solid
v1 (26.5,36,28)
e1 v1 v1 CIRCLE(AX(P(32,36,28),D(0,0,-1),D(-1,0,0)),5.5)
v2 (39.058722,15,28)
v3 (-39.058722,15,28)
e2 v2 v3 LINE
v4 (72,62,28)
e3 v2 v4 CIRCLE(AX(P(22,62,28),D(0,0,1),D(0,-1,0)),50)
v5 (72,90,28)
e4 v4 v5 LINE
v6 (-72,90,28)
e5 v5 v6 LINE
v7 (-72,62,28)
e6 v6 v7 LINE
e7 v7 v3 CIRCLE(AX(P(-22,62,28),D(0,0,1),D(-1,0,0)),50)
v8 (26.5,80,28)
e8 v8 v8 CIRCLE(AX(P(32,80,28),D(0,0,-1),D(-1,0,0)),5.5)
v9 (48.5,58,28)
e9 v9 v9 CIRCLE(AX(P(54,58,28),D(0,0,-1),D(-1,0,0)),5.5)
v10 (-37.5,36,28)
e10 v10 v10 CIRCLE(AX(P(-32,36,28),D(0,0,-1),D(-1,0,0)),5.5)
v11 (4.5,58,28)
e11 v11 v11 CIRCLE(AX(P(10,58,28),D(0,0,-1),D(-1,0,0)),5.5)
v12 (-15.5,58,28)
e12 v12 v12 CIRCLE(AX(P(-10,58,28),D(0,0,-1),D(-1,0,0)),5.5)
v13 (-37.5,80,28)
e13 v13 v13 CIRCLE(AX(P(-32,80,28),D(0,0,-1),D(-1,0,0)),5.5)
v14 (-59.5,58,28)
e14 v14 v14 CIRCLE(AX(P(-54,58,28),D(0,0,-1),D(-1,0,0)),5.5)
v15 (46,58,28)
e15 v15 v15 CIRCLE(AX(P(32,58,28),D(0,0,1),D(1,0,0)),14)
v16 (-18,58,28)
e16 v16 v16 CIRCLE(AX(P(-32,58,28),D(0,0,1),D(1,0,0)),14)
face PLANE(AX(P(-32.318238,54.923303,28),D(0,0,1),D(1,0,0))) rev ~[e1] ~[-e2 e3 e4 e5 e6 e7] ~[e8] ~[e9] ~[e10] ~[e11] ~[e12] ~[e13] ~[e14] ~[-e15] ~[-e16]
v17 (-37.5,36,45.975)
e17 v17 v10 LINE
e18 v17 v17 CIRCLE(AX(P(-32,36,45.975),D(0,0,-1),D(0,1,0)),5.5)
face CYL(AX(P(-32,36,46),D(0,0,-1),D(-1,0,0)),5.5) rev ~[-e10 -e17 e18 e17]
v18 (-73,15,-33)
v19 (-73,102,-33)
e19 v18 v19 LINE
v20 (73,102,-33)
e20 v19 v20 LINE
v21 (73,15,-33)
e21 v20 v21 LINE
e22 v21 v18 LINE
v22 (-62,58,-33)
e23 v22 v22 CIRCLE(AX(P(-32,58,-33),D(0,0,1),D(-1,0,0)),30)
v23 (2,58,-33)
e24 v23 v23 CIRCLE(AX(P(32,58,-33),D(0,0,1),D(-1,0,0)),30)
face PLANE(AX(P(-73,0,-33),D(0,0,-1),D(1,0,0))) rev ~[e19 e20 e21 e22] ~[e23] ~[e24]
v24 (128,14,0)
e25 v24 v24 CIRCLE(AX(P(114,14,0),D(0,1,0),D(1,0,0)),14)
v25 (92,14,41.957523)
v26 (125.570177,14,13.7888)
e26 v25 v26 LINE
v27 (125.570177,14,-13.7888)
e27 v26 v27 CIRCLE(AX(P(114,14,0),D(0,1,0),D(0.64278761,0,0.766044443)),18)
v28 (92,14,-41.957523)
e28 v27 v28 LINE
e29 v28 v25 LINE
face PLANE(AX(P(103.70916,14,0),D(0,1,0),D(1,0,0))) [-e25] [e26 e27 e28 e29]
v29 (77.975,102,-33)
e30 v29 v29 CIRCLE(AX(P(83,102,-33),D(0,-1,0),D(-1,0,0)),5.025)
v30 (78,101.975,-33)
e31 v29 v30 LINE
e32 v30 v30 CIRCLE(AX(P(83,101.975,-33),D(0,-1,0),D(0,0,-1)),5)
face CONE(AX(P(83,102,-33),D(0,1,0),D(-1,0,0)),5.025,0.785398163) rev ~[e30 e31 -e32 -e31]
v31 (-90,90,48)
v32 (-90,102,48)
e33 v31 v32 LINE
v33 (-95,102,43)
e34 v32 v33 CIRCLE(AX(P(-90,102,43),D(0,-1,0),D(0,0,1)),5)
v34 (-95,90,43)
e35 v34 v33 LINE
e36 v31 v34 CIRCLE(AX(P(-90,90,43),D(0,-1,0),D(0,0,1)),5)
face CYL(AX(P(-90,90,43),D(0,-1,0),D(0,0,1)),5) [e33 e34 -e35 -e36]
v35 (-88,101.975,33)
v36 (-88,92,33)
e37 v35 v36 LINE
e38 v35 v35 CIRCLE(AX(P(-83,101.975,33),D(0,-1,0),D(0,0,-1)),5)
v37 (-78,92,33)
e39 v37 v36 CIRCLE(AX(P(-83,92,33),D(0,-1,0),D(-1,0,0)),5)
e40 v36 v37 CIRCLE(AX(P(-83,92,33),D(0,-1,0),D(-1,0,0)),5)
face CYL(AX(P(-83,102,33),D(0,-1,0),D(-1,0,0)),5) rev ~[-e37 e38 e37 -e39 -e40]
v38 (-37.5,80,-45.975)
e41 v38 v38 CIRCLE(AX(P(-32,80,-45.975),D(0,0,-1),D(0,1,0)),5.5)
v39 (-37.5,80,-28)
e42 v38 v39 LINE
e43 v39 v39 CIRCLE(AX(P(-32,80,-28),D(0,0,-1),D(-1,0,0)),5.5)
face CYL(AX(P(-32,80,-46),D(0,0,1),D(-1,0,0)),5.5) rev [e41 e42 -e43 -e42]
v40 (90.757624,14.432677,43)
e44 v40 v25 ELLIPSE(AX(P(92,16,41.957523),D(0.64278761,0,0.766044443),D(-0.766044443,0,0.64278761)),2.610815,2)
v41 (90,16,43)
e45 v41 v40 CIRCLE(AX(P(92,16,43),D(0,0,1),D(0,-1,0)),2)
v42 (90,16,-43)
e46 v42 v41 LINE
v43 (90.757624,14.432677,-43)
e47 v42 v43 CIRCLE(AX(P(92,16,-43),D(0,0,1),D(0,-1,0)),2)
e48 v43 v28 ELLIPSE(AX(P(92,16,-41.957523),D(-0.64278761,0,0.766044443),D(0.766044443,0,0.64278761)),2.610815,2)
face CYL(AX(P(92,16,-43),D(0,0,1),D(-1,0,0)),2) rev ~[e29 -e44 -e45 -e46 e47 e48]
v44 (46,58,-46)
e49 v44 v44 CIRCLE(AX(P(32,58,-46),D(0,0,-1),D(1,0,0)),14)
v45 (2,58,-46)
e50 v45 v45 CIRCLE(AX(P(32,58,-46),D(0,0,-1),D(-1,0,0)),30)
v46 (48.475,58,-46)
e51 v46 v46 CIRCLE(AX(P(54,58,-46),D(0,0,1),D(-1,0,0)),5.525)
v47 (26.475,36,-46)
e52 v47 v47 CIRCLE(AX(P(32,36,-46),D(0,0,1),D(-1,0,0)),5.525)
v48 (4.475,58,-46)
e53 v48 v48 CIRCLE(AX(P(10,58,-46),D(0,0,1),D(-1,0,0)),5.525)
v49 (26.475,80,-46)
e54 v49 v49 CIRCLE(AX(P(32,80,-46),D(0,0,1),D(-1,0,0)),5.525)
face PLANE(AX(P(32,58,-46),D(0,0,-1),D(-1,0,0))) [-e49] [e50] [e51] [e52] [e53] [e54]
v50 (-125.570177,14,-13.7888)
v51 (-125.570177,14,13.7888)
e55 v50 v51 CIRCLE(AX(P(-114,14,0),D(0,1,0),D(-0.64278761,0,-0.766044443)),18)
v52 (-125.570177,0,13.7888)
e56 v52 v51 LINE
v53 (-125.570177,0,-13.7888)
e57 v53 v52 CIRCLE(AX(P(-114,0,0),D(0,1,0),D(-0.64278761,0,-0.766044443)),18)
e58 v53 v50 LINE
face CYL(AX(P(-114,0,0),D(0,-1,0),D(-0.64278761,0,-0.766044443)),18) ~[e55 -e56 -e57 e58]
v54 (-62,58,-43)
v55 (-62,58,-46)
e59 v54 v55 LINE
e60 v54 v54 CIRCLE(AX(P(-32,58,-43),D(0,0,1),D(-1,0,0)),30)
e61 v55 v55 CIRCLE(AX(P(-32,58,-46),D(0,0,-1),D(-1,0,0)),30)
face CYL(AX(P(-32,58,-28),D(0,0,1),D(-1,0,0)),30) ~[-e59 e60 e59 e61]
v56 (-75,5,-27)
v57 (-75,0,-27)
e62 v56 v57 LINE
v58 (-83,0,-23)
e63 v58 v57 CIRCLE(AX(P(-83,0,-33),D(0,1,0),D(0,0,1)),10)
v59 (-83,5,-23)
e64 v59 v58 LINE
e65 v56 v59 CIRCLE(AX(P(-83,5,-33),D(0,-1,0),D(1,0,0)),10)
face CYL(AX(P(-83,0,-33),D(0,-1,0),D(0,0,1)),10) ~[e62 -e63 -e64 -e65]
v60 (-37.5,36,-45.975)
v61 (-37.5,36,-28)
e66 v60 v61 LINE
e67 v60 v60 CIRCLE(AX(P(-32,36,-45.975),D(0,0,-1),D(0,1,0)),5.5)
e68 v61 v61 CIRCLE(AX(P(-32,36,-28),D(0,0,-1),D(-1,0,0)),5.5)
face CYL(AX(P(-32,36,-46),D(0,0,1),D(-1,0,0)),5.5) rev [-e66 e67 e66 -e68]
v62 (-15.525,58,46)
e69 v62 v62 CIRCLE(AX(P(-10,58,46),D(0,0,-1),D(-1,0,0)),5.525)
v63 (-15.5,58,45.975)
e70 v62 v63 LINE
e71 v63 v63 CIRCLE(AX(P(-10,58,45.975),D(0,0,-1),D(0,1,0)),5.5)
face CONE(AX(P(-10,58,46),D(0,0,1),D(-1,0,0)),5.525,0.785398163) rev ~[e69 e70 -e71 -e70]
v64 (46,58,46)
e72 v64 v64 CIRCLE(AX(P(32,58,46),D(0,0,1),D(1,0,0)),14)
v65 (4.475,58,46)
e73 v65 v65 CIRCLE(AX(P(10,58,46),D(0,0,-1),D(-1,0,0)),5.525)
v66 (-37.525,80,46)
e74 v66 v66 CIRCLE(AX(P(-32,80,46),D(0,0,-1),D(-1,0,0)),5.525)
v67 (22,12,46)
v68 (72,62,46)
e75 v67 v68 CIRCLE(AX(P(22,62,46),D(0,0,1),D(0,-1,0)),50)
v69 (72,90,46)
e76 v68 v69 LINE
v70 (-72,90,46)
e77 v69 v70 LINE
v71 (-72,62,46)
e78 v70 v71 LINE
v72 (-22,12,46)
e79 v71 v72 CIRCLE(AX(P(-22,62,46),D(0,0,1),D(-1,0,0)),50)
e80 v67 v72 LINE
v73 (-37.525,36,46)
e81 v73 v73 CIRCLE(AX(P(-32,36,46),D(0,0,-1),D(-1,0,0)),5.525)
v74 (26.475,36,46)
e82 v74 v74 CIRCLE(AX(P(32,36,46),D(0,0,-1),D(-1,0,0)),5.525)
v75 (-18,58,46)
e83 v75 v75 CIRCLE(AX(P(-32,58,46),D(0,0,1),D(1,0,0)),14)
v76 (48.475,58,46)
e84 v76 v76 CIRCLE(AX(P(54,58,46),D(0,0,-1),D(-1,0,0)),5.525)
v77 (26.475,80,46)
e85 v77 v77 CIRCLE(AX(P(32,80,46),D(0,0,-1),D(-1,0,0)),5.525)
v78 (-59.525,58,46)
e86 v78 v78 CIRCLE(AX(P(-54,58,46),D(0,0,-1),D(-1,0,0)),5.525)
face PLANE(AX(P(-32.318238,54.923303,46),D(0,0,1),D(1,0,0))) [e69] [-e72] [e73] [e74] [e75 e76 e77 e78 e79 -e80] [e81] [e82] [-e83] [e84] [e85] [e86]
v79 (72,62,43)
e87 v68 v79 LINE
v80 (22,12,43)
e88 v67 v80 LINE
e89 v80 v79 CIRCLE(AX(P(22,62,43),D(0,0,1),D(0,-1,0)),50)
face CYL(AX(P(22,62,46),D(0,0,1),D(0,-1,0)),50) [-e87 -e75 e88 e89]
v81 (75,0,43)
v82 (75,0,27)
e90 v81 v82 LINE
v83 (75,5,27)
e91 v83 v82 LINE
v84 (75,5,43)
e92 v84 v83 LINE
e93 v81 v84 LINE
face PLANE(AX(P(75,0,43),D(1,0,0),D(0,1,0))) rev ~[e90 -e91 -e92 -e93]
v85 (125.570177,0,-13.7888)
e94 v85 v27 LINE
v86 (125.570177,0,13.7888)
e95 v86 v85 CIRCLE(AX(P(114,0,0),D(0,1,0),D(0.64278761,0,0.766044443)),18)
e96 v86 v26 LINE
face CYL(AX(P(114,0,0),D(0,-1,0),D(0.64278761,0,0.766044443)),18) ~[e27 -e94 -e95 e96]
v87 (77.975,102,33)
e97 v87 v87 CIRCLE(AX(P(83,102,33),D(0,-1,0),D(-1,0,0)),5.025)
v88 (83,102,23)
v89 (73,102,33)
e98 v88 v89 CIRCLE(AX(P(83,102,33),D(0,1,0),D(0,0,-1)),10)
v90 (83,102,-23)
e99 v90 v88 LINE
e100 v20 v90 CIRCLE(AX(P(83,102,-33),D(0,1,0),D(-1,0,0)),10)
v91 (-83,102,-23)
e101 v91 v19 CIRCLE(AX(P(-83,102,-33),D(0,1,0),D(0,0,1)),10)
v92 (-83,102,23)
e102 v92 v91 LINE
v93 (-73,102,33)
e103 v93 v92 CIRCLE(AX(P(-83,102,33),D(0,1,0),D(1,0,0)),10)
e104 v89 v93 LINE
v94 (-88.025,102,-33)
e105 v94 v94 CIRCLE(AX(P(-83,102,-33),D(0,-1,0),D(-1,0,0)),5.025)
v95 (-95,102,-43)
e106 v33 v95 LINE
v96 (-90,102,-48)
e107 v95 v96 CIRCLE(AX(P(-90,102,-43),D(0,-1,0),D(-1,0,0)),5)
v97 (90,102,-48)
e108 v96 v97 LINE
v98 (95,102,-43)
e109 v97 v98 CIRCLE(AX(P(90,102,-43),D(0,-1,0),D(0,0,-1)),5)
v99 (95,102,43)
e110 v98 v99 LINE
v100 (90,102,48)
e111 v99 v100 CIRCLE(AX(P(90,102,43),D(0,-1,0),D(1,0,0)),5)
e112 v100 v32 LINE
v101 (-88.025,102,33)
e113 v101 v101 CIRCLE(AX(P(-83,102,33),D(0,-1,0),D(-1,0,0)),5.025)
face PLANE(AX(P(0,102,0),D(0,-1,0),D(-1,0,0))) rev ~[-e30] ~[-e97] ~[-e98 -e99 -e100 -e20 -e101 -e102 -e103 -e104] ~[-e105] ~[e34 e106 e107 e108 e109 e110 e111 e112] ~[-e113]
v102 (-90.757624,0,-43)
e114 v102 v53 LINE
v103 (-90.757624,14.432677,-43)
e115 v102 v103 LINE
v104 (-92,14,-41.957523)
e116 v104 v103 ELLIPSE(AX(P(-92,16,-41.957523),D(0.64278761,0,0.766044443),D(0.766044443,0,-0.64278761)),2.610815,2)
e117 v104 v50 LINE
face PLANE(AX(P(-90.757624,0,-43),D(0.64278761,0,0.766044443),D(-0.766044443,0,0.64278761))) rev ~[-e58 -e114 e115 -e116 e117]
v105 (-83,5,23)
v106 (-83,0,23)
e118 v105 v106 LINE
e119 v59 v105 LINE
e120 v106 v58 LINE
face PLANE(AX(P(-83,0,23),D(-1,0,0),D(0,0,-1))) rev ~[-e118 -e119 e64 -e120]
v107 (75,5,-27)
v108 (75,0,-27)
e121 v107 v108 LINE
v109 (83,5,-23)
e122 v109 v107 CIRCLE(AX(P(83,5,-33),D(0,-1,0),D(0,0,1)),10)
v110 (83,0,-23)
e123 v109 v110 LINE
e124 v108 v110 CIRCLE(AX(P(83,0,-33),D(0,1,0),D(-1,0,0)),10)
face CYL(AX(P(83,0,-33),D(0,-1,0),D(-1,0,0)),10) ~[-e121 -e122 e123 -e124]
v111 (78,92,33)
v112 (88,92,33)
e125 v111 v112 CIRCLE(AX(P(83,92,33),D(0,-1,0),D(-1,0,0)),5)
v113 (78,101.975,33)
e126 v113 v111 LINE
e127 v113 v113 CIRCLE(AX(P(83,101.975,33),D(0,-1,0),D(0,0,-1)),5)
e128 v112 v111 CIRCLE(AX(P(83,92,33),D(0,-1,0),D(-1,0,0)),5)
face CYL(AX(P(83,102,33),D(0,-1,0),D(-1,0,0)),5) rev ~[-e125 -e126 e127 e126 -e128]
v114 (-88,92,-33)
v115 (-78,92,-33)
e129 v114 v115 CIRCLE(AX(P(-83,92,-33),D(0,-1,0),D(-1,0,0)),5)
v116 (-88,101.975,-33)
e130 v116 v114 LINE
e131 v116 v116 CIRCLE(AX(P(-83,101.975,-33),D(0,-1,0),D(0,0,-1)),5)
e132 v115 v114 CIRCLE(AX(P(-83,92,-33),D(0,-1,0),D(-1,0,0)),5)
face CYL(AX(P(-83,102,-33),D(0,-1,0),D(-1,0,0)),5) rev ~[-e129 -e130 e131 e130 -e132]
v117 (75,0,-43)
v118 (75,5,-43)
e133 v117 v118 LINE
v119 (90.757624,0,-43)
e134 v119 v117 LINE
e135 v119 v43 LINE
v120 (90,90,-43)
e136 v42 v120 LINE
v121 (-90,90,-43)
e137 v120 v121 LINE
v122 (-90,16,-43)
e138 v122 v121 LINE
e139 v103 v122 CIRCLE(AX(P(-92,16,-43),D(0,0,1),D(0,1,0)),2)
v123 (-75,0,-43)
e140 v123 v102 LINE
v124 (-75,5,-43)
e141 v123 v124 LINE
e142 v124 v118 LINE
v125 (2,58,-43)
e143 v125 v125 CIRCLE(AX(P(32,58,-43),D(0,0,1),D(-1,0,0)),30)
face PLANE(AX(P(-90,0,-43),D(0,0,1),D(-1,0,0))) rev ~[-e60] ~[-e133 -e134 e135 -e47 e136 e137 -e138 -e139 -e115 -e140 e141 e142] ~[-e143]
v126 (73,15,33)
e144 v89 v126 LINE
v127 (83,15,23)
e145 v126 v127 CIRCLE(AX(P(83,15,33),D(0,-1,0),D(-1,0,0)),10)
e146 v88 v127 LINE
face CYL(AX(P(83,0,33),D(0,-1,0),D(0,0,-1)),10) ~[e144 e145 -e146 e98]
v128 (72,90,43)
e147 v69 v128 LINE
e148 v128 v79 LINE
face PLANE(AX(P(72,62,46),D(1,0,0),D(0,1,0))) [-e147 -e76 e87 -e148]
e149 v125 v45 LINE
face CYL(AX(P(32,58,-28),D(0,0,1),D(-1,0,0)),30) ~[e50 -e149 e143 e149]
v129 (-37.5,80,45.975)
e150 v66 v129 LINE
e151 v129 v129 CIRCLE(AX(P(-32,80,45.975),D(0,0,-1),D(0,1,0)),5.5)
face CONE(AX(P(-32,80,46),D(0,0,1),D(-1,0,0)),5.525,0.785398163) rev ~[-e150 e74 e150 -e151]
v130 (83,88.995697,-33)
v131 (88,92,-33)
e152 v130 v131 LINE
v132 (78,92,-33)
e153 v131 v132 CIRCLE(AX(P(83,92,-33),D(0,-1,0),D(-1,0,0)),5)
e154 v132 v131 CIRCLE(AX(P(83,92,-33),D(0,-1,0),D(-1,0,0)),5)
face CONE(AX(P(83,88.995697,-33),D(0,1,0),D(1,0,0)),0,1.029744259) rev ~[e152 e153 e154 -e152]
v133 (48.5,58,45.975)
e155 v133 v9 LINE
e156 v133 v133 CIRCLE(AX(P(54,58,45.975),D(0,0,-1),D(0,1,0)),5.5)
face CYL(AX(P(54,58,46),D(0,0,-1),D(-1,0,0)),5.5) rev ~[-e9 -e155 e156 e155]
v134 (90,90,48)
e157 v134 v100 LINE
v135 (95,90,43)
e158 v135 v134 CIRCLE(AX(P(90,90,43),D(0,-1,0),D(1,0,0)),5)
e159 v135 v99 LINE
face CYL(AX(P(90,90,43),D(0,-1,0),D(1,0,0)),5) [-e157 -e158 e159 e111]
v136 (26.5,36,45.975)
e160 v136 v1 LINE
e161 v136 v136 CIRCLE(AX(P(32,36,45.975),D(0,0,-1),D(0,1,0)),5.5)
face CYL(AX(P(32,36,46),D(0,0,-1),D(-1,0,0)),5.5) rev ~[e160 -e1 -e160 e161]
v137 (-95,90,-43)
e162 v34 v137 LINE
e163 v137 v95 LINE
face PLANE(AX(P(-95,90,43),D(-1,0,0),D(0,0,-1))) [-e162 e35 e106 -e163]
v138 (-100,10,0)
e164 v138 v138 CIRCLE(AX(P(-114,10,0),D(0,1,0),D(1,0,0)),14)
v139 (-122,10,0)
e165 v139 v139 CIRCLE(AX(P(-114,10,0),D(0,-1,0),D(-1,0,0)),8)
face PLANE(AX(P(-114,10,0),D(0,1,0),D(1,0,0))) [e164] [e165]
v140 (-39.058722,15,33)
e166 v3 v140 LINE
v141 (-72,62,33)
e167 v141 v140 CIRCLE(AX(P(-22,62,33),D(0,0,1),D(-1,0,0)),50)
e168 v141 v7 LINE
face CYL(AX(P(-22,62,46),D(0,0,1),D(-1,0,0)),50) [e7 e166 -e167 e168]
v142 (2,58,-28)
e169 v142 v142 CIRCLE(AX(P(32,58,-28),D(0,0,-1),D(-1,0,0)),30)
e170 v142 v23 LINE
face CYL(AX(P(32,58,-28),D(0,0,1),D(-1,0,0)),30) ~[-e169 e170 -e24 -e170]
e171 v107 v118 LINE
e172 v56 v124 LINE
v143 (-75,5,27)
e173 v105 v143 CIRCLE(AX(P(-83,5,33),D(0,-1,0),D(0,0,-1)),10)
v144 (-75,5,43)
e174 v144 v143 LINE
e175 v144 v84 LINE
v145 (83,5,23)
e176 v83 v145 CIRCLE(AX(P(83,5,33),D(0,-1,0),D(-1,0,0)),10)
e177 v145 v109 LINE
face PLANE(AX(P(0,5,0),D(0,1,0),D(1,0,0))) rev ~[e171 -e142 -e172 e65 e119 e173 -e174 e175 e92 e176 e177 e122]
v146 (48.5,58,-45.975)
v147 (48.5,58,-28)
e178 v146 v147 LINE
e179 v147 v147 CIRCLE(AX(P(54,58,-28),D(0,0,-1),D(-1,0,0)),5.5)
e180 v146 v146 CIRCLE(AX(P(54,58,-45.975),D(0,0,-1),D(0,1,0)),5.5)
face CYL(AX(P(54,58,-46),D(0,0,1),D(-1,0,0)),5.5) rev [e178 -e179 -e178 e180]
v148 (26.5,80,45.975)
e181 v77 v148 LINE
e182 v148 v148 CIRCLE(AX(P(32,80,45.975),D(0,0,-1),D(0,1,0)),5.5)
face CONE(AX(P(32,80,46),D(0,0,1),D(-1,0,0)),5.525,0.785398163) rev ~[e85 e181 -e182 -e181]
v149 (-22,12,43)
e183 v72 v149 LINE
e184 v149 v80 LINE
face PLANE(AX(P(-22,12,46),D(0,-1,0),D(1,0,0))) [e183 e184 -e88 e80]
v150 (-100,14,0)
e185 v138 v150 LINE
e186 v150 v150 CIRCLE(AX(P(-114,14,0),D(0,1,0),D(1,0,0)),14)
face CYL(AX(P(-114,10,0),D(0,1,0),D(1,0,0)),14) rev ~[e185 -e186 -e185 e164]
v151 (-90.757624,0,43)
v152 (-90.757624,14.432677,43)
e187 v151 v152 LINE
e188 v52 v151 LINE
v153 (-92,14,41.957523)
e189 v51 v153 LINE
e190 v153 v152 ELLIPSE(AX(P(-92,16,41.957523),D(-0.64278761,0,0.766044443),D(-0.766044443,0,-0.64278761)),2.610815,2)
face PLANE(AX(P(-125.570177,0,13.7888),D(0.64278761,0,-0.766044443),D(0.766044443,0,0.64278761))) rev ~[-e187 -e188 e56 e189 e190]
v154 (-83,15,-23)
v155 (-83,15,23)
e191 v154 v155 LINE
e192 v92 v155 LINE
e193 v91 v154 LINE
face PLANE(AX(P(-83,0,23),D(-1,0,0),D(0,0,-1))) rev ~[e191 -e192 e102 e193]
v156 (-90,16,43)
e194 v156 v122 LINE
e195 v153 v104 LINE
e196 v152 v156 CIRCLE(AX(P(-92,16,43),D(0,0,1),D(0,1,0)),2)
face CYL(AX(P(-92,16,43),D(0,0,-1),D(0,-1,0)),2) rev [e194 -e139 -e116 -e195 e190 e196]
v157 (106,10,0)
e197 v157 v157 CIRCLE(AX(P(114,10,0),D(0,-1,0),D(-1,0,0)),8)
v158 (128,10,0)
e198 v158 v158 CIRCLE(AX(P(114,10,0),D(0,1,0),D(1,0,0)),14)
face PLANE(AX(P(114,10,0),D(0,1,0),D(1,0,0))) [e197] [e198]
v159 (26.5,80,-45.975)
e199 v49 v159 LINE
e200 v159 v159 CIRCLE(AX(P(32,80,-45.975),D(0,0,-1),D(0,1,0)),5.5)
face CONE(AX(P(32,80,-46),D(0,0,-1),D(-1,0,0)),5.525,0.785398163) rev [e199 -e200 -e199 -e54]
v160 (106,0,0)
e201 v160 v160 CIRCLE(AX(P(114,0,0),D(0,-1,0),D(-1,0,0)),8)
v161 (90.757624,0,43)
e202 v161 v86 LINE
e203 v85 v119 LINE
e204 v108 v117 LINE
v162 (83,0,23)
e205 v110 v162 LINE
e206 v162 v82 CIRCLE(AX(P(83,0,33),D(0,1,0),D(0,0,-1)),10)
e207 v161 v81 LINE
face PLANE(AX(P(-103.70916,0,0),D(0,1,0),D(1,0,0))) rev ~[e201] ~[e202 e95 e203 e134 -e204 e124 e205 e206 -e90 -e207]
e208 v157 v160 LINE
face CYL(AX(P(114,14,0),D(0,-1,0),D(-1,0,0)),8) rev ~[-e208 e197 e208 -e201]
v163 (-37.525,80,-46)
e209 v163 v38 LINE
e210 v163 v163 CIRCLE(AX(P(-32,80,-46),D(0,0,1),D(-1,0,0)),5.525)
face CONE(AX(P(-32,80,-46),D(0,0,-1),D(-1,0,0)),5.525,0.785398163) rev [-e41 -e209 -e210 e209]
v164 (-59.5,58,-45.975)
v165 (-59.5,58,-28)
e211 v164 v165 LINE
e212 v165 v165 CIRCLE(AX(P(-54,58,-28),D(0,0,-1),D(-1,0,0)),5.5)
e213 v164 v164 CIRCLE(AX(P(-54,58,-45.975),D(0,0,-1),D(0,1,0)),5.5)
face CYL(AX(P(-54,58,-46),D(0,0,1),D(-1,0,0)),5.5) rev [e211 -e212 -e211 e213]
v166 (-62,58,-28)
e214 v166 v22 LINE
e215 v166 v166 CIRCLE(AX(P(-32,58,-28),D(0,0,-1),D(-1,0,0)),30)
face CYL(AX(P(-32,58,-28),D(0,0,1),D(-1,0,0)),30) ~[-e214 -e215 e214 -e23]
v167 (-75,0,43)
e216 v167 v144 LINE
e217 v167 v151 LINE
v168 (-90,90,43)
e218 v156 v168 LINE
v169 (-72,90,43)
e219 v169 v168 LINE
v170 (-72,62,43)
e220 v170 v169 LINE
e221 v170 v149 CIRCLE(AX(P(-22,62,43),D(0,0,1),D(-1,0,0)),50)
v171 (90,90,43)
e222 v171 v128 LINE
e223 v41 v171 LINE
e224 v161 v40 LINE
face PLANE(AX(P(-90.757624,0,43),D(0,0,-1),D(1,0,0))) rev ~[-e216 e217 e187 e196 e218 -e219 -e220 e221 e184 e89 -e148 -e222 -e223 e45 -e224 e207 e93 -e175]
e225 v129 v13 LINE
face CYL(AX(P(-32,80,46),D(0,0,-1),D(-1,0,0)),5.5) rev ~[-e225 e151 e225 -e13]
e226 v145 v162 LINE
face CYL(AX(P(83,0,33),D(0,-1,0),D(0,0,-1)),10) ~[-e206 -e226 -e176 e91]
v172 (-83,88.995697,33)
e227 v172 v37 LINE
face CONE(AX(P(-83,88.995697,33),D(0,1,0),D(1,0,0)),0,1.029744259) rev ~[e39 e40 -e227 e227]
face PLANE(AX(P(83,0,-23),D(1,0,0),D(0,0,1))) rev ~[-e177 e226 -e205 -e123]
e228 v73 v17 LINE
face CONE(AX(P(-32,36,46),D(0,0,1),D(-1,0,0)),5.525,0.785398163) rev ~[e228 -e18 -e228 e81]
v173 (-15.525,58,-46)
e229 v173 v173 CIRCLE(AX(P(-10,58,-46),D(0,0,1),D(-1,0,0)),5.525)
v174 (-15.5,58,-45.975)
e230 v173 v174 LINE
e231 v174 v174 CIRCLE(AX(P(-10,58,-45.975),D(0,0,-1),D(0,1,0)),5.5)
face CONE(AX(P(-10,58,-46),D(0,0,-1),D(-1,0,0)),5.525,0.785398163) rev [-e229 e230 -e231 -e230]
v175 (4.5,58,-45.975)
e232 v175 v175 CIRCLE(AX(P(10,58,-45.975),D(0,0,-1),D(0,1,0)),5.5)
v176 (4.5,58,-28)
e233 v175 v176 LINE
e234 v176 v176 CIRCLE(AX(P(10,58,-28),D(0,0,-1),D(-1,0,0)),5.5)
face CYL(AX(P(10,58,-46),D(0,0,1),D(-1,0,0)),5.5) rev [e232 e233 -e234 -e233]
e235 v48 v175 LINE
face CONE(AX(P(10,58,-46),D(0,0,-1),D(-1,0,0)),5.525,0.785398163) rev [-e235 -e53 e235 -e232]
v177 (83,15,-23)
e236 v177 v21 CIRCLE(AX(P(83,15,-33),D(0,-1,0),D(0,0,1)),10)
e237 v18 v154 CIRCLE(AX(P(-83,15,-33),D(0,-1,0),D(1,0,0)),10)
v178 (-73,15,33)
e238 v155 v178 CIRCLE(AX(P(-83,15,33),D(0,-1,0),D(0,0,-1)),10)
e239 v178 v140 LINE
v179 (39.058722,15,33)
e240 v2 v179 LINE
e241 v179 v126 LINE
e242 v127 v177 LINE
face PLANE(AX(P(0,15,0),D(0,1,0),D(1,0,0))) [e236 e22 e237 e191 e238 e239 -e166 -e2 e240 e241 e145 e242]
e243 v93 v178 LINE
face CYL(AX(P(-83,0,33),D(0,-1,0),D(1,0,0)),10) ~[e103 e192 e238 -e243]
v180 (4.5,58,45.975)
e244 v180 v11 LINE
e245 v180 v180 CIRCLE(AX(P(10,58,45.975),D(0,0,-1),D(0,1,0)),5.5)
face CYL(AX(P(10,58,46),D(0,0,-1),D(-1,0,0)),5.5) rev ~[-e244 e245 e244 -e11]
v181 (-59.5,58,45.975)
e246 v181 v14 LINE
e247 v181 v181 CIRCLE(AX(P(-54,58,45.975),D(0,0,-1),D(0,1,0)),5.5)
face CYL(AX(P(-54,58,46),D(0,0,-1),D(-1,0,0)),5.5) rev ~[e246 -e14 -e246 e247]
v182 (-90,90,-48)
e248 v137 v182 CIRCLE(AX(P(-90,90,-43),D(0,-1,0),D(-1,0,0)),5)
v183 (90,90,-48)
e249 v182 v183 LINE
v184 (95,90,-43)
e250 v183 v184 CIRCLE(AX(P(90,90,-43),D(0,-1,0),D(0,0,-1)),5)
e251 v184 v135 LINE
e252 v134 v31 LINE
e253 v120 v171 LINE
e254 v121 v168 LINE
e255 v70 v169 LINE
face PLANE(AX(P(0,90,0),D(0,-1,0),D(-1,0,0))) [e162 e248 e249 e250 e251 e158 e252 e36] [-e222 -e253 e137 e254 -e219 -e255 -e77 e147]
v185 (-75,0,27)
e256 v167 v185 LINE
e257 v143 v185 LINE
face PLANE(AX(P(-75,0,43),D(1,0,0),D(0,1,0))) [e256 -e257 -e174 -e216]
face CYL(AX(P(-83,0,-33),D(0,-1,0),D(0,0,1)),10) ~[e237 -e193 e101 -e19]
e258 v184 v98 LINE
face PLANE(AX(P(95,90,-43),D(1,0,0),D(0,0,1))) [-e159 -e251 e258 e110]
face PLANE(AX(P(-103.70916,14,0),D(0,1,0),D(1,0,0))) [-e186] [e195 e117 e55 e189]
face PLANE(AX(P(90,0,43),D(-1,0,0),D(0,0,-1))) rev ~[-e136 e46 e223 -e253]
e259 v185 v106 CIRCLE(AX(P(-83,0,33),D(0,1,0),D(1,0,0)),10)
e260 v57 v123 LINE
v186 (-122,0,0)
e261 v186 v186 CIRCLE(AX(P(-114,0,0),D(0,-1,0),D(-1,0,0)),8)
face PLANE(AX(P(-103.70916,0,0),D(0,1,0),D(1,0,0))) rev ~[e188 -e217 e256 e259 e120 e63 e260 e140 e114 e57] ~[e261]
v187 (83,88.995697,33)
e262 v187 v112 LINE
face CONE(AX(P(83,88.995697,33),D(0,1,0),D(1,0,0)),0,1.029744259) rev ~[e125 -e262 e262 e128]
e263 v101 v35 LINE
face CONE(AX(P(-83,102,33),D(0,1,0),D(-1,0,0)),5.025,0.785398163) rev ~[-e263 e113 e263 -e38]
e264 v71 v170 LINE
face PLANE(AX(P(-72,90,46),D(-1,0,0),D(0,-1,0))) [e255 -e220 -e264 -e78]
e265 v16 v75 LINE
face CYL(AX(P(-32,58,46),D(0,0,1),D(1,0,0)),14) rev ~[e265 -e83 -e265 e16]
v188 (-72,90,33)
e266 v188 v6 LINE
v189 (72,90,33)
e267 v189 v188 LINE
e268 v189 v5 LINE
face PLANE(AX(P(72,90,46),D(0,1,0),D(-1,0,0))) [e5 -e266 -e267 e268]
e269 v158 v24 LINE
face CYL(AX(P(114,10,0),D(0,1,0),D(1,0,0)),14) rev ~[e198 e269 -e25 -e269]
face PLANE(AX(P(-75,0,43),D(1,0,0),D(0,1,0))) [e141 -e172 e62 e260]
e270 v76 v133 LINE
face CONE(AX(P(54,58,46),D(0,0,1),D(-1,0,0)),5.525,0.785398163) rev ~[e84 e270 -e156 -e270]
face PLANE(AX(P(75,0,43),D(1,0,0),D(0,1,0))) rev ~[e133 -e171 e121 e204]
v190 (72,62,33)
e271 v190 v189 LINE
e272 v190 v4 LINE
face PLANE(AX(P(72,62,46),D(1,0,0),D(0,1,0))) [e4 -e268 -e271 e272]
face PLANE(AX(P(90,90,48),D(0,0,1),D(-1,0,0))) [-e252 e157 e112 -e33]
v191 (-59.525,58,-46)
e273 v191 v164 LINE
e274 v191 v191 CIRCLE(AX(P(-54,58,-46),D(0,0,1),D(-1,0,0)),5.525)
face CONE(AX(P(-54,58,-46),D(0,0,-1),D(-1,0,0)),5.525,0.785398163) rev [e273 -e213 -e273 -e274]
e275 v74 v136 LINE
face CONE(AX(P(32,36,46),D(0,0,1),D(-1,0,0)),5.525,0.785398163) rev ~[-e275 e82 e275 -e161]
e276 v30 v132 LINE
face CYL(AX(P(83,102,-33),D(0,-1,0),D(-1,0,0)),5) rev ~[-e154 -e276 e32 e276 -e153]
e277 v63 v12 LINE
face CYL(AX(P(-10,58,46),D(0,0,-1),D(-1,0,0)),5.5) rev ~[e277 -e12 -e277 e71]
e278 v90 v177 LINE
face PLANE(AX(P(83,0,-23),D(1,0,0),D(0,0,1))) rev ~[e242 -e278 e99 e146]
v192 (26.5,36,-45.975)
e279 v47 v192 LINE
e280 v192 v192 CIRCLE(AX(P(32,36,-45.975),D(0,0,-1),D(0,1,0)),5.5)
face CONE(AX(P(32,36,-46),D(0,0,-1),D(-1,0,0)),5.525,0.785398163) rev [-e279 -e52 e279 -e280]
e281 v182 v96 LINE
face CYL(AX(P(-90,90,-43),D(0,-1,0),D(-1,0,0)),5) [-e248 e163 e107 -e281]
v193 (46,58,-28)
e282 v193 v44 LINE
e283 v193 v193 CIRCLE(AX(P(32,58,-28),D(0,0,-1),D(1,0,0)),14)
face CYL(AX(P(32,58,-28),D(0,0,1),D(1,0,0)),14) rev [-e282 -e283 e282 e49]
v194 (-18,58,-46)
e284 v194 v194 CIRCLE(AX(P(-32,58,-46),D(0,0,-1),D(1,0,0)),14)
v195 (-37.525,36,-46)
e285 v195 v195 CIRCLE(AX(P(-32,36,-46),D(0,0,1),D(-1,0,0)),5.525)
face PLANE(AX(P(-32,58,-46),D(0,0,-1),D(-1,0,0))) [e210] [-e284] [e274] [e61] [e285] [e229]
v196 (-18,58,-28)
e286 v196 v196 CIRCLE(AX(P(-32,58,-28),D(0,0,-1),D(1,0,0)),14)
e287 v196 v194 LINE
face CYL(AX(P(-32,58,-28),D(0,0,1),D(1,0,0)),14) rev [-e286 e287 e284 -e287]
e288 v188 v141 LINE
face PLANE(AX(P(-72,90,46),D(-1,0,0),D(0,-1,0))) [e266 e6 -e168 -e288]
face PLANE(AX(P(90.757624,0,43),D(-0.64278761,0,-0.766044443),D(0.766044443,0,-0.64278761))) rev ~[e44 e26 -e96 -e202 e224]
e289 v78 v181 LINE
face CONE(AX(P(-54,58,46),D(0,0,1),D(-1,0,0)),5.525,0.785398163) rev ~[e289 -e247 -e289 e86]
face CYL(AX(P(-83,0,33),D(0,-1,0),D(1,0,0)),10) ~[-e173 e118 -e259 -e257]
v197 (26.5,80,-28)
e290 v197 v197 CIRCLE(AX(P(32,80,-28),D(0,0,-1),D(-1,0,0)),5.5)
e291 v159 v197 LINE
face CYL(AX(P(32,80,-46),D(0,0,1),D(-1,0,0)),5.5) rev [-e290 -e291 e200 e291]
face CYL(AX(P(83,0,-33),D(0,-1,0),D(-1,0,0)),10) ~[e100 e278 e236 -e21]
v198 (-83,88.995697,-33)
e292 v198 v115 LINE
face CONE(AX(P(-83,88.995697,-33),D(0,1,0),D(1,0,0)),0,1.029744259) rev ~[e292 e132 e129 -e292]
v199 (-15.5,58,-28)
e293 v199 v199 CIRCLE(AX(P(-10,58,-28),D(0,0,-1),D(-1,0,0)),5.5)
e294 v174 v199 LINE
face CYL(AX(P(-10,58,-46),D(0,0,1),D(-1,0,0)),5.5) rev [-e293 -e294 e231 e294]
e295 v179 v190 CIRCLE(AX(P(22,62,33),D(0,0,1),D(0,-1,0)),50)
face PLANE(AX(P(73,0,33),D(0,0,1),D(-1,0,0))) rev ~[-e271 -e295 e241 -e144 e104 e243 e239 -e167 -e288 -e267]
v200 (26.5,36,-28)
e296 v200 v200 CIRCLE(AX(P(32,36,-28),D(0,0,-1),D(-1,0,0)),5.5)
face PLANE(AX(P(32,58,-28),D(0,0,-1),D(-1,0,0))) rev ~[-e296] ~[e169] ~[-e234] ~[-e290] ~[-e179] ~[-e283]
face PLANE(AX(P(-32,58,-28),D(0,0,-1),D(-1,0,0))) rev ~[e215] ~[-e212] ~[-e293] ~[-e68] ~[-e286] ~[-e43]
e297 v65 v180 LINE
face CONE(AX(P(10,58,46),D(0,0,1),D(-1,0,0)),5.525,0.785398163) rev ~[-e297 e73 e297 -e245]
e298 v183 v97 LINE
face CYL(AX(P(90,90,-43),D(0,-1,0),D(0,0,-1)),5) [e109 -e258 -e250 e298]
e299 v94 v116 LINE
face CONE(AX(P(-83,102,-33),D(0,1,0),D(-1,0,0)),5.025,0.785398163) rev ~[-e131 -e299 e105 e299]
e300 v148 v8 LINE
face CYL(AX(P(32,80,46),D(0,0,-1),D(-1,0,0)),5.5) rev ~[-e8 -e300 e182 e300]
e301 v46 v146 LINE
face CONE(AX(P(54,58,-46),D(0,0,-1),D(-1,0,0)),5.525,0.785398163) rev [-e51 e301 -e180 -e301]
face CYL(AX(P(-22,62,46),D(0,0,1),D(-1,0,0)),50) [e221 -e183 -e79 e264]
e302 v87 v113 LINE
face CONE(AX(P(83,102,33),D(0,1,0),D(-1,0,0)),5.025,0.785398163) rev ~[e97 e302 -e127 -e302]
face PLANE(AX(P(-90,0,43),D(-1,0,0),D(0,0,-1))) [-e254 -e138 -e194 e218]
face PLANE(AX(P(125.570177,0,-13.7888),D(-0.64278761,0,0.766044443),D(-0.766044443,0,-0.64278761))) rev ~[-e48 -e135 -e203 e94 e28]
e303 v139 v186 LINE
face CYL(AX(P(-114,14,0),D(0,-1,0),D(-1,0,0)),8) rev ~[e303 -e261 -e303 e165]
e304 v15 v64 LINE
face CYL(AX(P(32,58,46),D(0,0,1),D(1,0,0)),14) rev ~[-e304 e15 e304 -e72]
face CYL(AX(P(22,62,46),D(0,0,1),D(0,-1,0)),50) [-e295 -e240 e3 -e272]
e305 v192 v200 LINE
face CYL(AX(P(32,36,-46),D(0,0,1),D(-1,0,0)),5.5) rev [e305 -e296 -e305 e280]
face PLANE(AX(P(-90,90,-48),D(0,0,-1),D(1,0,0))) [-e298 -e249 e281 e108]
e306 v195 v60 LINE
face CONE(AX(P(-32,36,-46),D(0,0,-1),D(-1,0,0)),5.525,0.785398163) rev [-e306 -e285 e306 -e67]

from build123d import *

# Parameters (mm, degrees)
HOUSING_BASE_PROFILE_SKETCH_W          = 180
HOUSING_BASE_PROFILE_SKETCH_H          = 86
HOUSING_BODY_DEPTH                     = 102
TOP_START                              = -12
TOP_FLANGE_DEPTH                       = 12
MOUNTING_FOOT_LUGS_DEPTH               = 14
SIDE_START                             = 3
SIDE_FLANGE_PAD_SKETCH_R               = 14
SIDE_FLANGE_PADS_DEPTH                 = 18
BEARING_START                          = -15
BEARING_BOSS_60_SKETCH_R               = 30
BEARING_BOSS_60_SKETCH_R_2             = 14
BEARING_BOSSES_60_DEPTH                = 18
SKETCH6_2_R                            = 14
BEARING_BORES_DEPTH                    = 191.023682735
HOUSING_CAVITY_SKETCH_W                = 150
HOUSING_CAVITY_SKETCH_H                = 5
HOUSING_CAVITY_DEPTH                   = 191.023682735
BASE_START                             = 5
BASE_PROFILE_PAD_10MM_DEPTH            = 10
FOOT_COUNTERBORED_HOLES_16_D           = 16
FOOT_COUNTERBORED_HOLES_16_CBORE_D     = 28
FOOT_COUNTERBORED_HOLES_16_CBORE_DEPTH = 4
DOWEL_HOLES_10_D                       = 10
DOWEL_HOLES_10_DEPTH                   = 10
DOWEL_HOLES_10_CSINK_D                 = 10.05
DOWEL_HOLES_10_CSINK_ANGLE             = 90
DOWEL_HOLES_10_TIP                     = 3.004303095
FLANGE_BOLT_HOLES_M10_D                = 11
FLANGE_BOLT_HOLES_M10_DEPTH            = 18
FLANGE_BOLT_HOLES_M10_CSINK_D          = 11.05
FLANGE_BOLT_HOLES_M10_CSINK_ANGLE      = 90
FOOT_FILLETS_R2_R                      = 2


with BuildPart() as part:
    # Housing Base Profile Sketch → Housing Body (new body)
    with BuildSketch(Plane(origin=(0, 0, 0), x_dir=(1, 0, 0), z_dir=(0, 1, 0))):
        Rectangle(HOUSING_BASE_PROFILE_SKETCH_W, HOUSING_BASE_PROFILE_SKETCH_H)
        with BuildLine():
            Line((-73, 33), (73, 33))
            ThreePointArc((73, 33), (75.928932188, 25.928932188), (83, 23))
            Line((83, 23), (83, -23))
            ThreePointArc((83, -23), (75.928932188, -25.928932188), (73, -33))
            Line((73, -33), (-73, -33))
            ThreePointArc((-73, -33), (-75.928932188, -25.928932188), (-83, -23))
            Line((-83, -23), (-83, 23))
            ThreePointArc((-83, 23), (-75.928932188, 25.928932188), (-73, 33))
        make_face(mode=Mode.SUBTRACT)
    extrude(amount=HOUSING_BODY_DEPTH)

    # Top Flange Sketch → Top Flange (add)
    with BuildSketch(Plane(origin=(0, 102, 0), x_dir=(1, 0, 0), z_dir=(0, 1, 0)).offset(TOP_START)):
        with BuildLine():
            Line((-90, 48), (90, 48))
            ThreePointArc((90, 48), (93.535533906, 46.535533906), (95, 43))
            Line((95, 43), (95, -43))
            ThreePointArc((95, -43), (93.535533906, -46.535533906), (90, -48))
            Line((90, -48), (-90, -48))
            ThreePointArc((-90, -48), (-93.535533906, -46.535533906), (-95, -43))
            Line((-95, -43), (-95, 43))
            ThreePointArc((-95, 43), (-93.535533906, 46.535533906), (-90, 48))
        make_face()
        with BuildLine():
            Line((-73, 33), (73, 33))
            ThreePointArc((73, 33), (75.928932188, 25.928932188), (83, 23))
            Line((83, 23), (83, -23))
            ThreePointArc((83, -23), (75.928932188, -25.928932188), (73, -33))
            Line((73, -33), (-73, -33))
            ThreePointArc((-73, -33), (-75.928932188, -25.928932188), (-83, -23))
            Line((-83, -23), (-83, 23))
            ThreePointArc((-83, 23), (-75.928932188, 25.928932188), (-73, 33))
        make_face(mode=Mode.SUBTRACT)
    extrude(amount=TOP_FLANGE_DEPTH)

    # Sketch2_4 → Mounting Foot Lugs (add)
    with BuildSketch(Plane(origin=(0, 0, 0), x_dir=(1, 0, 0), z_dir=(0, 1, 0))):
        with BuildLine():
            Line((-90, -43), (-90, 43))
            Line((-90, 43), (-90.757624402, 43))
            Line((-90.757624402, 43), (-125.570176974, 13.788799976))
            ThreePointArc((-125.570176974, 13.788799976), (-132, 0), (-125.570176974, -13.788799976))
            Line((-125.570176974, -13.788799976), (-90.757624402, -43))
            Line((-90.757624402, -43), (-90, -43))
        make_face()
        with BuildLine():
            Line((90.757624402, 43), (90, 43))
            Line((90, 43), (90, -43))
            Line((90, -43), (90.757624402, -43))
            Line((90.757624402, -43), (125.570176974, -13.788799976))
            ThreePointArc((125.570176974, -13.788799976), (132, 0), (125.570176974, 13.788799976))
            Line((125.570176974, 13.788799976), (90.757624402, 43))
        make_face()
    extrude(amount=MOUNTING_FOOT_LUGS_DEPTH)

    # Side Flange Pad Sketch → Side Flange Pads (add)
    # profile 1 of 2: a face of its own
    with BuildSketch(Plane.XY.offset(43).offset(SIDE_START)):
        with BuildLine():
            Line((-22, 12), (0, 12))
            Line((0, 12), (0, 90))
            Line((0, 90), (-72, 90))
            Line((-72, 90), (-72, 62))
            ThreePointArc((-72, 62), (-57.355339059, 26.644660941), (-22, 12))
        make_face()
        with Locations((-32, 58)):
            Circle(SIDE_FLANGE_PAD_SKETCH_R, mode=Mode.SUBTRACT)
    # profile 2 of 2: a face of its own
    with BuildSketch(Plane.XY.offset(43).offset(SIDE_START)):
        with BuildLine():
            Line((0, 90), (0, 12))
            Line((0, 12), (22, 12))
            ThreePointArc((22, 12), (57.355339059, 26.644660941), (72, 62))
            Line((72, 62), (72, 90))
            Line((72, 90), (0, 90))
        make_face()
        with Locations((32, 58)):
            Circle(SIDE_FLANGE_PAD_SKETCH_R, mode=Mode.SUBTRACT)
    extrude(amount=-SIDE_FLANGE_PADS_DEPTH)

    # Bearing Boss _60 Sketch → Bearing Bosses _60 (add)
    # profile 1 of 2: a face of its own
    with BuildSketch(Plane(origin=(0, 0, -43), x_dir=(-1, 0, 0), z_dir=(0, 0, -1)).offset(BEARING_START)):
        with Locations((-32, 58)):
            Circle(BEARING_BOSS_60_SKETCH_R)
        with Locations(Location((-32, 58, 0), (0, 0, 180))):
            Circle(BEARING_BOSS_60_SKETCH_R_2, mode=Mode.SUBTRACT)
    # profile 2 of 2: a face of its own
    with BuildSketch(Plane(origin=(0, 0, -43), x_dir=(-1, 0, 0), z_dir=(0, 0, -1)).offset(BEARING_START)):
        with Locations((32, 58)):
            Circle(BEARING_BOSS_60_SKETCH_R)
        with Locations(Location((32, 58, 0), (0, 0, 180))):
            Circle(BEARING_BOSS_60_SKETCH_R_2, mode=Mode.SUBTRACT)
    extrude(amount=BEARING_BOSSES_60_DEPTH)

    # Sketch6_2 → Bearing Bores (cut, through all)
    with BuildSketch(Plane(origin=(0, 0, -43), x_dir=(-1, 0, 0), z_dir=(0, 0, -1))):
        with Locations(Location((32, 58, 0), (0, 0, 180))):
            Circle(SKETCH6_2_R)
        with Locations(Location((-32, 58, 0), (0, 0, 180))):
            Circle(SKETCH6_2_R)
    extrude(amount=-BEARING_BORES_DEPTH, mode=Mode.SUBTRACT)

    # Housing Cavity Sketch → Housing Cavity (cut, through all)
    with BuildSketch(Plane.XY.offset(43)):
        with Locations((0, 2.5)):
            Rectangle(HOUSING_CAVITY_SKETCH_W, HOUSING_CAVITY_SKETCH_H)
    extrude(amount=-HOUSING_CAVITY_DEPTH, mode=Mode.SUBTRACT)

    # Sketch2_5 → Base Profile Pad 10mm (add)
    with BuildSketch(Plane(origin=(0, 0, 0), x_dir=(1, 0, 0), z_dir=(0, 1, 0)).offset(BASE_START)):
        with BuildLine():
            Line((-83, 23), (-83, -23))
            ThreePointArc((-83, -23), (-75.928932188, -25.928932188), (-73, -33))
            Line((-73, -33), (73, -33))
            ThreePointArc((73, -33), (75.928932188, -25.928932188), (83, -23))
            Line((83, -23), (83, 23))
            ThreePointArc((83, 23), (75.928932188, 25.928932188), (73, 33))
            Line((73, 33), (-73, 33))
            ThreePointArc((-73, 33), (-75.928932188, 25.928932188), (-83, 23))
        make_face()
    extrude(amount=BASE_PROFILE_PAD_10MM_DEPTH)

    # Foot Counterbored Holes _16 (through all)
    with Locations(Plane(origin=(0, 14, 0), x_dir=(1, 0, 0), z_dir=(0, 1, 0))):
        with Locations((114, 0), (-114, 0)):
            CounterBoreHole(FOOT_COUNTERBORED_HOLES_16_D / 2, FOOT_COUNTERBORED_HOLES_16_CBORE_D / 2, FOOT_COUNTERBORED_HOLES_16_CBORE_DEPTH)

    # Dowel Holes _10
    with Locations(Plane(origin=(0, 102, 0), x_dir=(1, 0, 0), z_dir=(0, 1, 0))):
        with Locations((83, 33), (83, -33), (-83, -33), (-83, 33)):
            CounterSinkHole(DOWEL_HOLES_10_D / 2, DOWEL_HOLES_10_CSINK_D / 2, depth=DOWEL_HOLES_10_DEPTH, counter_sink_angle=DOWEL_HOLES_10_CSINK_ANGLE)
            with Locations((0, 0, -(DOWEL_HOLES_10_DEPTH + DOWEL_HOLES_10_TIP / 2))):  # 118° drill point
                Cone(0, DOWEL_HOLES_10_D / 2, DOWEL_HOLES_10_TIP, mode=Mode.SUBTRACT)

    # Flange Bolt Holes M10
    with Locations(Plane.XY.offset(46)):
        with Locations((54, 58), (-32, 80), (-10, 58), (-32, 36), (-54, 58), (32, 36), (10, 58), (32, 80)):
            flange_bolt_holes_m10 = CounterSinkHole(FLANGE_BOLT_HOLES_M10_D / 2, FLANGE_BOLT_HOLES_M10_CSINK_D / 2, depth=FLANGE_BOLT_HOLES_M10_DEPTH, counter_sink_angle=FLANGE_BOLT_HOLES_M10_CSINK_ANGLE)

    # Flange Bolt Holes Mirror: Flange Bolt Holes M10 across plane
    add(flange_bolt_holes_m10.mirror(Plane.XY), mode=Mode.SUBTRACT)

    # Foot Fillets R2
    foot_fillets_r2_edges = [part.edges().sort_by_distance(p)[0] for p in [
        (-90, 14, 0),
        (90, 14, 0),
    ]]
    fillet(foot_fillets_r2_edges, radius=FOOT_FILLETS_R2_R)


solid = part.part
